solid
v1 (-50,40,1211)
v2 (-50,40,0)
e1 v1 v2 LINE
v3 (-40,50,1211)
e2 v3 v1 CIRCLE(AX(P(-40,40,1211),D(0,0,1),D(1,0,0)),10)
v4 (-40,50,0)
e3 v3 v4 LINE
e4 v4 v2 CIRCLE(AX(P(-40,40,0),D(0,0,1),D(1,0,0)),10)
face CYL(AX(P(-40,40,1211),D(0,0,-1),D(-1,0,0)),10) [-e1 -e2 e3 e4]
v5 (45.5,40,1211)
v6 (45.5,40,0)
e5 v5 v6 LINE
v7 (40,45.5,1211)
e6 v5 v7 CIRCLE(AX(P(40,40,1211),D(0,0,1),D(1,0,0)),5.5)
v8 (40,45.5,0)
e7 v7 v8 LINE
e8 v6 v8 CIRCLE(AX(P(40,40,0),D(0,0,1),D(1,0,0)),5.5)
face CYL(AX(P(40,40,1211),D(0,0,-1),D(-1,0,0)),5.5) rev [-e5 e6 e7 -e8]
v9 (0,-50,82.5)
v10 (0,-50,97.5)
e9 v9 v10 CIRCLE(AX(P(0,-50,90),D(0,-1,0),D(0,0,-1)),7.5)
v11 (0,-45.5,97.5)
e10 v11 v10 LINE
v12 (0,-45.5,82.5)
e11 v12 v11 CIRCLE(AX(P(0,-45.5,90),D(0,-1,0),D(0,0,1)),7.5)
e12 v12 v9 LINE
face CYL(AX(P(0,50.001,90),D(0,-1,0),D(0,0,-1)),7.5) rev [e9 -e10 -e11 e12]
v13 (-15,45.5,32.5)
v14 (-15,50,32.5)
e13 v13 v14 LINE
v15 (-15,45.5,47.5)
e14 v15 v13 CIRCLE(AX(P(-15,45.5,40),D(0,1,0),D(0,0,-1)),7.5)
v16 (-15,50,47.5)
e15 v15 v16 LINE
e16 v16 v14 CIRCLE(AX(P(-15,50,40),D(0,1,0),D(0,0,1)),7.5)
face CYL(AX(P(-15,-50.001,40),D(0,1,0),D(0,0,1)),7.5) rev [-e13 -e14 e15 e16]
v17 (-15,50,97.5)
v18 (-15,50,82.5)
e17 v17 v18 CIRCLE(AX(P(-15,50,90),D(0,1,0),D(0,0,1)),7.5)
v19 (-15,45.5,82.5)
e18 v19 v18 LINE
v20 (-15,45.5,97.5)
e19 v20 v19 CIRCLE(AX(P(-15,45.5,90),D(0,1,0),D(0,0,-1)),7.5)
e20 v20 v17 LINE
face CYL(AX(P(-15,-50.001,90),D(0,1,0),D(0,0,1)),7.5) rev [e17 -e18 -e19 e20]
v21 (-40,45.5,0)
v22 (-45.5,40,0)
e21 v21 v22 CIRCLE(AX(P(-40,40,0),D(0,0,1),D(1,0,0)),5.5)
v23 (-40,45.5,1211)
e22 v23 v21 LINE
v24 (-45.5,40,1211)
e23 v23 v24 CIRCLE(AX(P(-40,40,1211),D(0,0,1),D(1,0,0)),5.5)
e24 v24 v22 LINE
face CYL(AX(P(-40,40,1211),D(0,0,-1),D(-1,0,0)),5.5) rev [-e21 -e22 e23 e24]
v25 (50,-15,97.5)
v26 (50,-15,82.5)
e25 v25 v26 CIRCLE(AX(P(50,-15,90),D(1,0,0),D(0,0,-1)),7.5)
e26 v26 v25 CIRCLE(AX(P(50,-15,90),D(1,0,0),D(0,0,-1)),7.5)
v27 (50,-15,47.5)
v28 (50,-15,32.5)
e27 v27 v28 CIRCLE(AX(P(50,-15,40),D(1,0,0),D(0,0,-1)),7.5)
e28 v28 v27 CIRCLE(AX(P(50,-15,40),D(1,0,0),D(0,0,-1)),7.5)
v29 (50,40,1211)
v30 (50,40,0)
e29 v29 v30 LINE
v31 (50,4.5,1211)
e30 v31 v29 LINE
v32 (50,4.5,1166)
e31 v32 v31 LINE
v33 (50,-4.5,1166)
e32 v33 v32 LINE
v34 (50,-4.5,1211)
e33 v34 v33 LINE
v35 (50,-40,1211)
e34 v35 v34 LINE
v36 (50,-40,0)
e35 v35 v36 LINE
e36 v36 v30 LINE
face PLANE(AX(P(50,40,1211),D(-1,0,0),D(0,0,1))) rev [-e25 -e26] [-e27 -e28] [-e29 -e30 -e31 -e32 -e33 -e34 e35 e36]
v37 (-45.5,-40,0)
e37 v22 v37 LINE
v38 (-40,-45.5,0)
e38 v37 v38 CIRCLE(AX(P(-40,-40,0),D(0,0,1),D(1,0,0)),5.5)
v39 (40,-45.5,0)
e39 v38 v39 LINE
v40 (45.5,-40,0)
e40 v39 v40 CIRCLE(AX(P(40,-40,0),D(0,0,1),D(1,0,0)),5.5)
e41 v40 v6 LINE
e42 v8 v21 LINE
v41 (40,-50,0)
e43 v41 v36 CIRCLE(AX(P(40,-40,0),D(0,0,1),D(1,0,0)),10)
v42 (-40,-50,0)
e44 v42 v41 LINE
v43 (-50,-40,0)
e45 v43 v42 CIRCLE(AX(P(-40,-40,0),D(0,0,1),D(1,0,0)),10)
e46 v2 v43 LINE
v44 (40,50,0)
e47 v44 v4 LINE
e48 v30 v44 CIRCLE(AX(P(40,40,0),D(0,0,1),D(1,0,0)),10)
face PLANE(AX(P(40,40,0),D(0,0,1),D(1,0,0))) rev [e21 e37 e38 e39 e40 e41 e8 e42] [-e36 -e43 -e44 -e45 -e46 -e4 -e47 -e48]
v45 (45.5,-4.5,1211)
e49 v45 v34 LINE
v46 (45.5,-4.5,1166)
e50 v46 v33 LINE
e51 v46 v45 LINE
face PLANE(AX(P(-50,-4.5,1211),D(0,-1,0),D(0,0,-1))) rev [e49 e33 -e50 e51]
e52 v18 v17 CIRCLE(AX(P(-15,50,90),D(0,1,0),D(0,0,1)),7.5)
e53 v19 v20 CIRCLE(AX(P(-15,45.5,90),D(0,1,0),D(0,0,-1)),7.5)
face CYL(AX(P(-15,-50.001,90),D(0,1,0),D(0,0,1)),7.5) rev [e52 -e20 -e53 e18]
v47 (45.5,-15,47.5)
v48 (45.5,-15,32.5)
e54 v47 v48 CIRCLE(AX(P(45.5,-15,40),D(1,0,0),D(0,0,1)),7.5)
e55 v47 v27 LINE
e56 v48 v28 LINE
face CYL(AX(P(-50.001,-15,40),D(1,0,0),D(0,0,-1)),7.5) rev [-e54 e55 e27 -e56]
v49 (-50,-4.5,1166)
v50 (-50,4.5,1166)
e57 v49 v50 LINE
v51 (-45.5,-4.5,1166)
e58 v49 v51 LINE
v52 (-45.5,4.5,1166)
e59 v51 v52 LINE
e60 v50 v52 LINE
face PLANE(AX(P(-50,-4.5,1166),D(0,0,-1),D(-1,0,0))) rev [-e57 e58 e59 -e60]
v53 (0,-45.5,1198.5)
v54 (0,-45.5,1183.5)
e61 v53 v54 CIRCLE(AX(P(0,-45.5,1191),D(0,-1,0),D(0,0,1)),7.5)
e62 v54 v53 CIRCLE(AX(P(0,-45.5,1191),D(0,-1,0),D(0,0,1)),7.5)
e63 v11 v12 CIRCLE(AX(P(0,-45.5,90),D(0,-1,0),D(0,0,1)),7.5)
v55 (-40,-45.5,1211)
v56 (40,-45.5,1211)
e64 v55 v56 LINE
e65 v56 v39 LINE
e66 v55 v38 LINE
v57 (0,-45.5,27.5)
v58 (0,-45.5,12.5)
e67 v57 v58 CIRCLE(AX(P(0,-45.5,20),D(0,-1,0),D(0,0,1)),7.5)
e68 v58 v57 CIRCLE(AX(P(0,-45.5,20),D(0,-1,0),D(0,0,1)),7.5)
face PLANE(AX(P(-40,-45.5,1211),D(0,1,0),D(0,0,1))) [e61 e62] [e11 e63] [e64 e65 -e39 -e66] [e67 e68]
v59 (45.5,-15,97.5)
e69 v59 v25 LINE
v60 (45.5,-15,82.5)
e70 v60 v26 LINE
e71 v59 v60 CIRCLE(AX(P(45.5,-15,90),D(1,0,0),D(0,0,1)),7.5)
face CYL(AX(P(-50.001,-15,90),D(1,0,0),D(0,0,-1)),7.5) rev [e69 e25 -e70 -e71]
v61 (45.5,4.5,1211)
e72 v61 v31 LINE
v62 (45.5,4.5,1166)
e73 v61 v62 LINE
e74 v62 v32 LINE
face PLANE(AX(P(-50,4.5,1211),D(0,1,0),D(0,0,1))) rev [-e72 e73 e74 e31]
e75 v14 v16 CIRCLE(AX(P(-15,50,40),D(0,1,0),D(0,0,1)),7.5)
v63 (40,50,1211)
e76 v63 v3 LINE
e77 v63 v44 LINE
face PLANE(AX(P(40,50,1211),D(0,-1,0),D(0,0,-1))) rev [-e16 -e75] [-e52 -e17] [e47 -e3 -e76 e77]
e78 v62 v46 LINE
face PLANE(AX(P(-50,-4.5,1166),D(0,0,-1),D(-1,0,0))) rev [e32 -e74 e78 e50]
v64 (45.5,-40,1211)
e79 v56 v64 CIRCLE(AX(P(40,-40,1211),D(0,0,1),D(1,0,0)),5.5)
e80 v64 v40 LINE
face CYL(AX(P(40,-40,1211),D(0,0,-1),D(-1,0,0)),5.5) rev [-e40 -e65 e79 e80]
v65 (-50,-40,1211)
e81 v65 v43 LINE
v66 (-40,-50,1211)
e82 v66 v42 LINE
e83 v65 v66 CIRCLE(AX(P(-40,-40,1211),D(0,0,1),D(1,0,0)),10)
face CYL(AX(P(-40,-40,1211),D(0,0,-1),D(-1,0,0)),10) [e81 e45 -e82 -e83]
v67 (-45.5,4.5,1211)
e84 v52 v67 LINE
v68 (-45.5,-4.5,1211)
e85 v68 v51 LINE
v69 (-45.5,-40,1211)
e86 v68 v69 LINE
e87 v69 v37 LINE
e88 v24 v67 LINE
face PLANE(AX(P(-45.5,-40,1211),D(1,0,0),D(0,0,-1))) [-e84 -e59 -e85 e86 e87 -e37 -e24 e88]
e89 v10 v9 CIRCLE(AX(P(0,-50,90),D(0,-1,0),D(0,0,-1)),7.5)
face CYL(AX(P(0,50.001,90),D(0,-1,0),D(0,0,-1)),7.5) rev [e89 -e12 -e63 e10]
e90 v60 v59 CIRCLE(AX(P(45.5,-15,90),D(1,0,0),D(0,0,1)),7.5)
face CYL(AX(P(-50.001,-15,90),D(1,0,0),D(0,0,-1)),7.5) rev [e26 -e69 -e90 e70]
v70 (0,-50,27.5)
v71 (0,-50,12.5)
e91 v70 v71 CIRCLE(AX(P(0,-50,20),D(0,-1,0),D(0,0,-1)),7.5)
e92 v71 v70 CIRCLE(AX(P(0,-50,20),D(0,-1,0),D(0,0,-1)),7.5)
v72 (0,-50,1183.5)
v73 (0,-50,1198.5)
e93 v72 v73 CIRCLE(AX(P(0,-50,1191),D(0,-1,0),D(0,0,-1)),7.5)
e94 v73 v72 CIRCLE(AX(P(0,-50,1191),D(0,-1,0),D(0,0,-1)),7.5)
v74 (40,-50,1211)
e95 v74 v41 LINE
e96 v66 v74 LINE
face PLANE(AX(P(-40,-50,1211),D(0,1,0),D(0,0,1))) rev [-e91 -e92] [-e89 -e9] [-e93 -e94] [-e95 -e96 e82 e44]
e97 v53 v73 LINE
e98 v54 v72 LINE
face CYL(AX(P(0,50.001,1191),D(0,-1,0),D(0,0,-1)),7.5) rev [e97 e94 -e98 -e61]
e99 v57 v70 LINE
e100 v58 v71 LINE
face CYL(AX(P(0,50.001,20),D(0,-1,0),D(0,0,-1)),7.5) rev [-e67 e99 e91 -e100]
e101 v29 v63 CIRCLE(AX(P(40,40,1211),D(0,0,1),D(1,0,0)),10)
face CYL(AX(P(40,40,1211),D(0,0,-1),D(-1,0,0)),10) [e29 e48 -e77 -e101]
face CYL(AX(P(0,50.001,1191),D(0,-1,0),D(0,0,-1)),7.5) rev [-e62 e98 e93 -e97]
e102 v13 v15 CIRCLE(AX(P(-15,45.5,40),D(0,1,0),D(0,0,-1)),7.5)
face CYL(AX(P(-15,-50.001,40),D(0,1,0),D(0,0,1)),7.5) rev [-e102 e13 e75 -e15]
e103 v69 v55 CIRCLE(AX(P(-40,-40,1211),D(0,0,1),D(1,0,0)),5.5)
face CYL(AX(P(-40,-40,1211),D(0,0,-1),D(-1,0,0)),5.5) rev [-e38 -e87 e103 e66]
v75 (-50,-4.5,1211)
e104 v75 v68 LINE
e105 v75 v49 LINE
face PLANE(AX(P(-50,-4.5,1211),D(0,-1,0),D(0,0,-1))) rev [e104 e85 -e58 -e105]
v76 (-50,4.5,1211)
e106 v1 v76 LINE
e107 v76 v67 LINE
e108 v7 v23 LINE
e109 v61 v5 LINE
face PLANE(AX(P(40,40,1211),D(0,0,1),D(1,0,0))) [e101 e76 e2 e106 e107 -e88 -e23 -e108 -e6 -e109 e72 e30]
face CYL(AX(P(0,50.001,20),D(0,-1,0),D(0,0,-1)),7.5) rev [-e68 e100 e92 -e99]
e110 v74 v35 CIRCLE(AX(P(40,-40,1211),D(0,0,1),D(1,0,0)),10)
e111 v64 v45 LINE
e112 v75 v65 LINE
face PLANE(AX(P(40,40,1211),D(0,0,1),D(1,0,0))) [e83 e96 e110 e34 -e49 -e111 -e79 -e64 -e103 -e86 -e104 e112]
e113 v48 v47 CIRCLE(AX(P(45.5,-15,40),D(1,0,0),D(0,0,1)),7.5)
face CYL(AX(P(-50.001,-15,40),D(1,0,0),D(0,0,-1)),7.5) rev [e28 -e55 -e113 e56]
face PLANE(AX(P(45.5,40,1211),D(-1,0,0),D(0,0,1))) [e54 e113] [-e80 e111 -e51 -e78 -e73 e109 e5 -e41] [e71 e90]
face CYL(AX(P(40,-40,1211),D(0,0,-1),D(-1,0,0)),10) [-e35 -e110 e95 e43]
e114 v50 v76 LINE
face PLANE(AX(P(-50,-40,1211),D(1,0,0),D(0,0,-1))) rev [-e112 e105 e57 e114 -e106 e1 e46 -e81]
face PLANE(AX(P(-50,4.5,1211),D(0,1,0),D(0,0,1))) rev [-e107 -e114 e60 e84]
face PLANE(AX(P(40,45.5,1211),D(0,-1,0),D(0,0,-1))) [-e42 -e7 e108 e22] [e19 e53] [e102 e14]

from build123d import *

# Parameters (mm, degrees)
BOSS_EXTRUDE1_DEPTH = 1211
CUT_EXTRUDE1_REACH  = 1218.15
SKETCH_1_R          = 7.5
CUT_EXTRUDE2_REACH  = 1218.15
SKETCH2_R           = 7.5
CUT_EXTRUDE3_REACH  = 1218.15
SKETCH3_R           = 7.5
SKETCH4_W           = 45
SKETCH4_H           = 9
CUT_EXTRUDE4_DEPTH  = 1217.150072976


with BuildPart() as part:
    # Sketch1 → Boss-Extrude1 (new body)
    with BuildSketch(Plane.XY):
        with BuildLine():
            Line((-40, -50), (40, -50))
            ThreePointArc((40, -50), (47.071067812, -47.071067812), (50, -40))
            Line((50, -40), (50, 40))
            ThreePointArc((50, 40), (47.071067812, 47.071067812), (40, 50))
            Line((40, 50), (-40, 50))
            ThreePointArc((-40, 50), (-47.071067812, 47.071067812), (-50, 40))
            Line((-50, 40), (-50, -40))
            ThreePointArc((-50, -40), (-47.071067812, -47.071067812), (-40, -50))
        make_face()
        with BuildLine():
            Line((-40, -45.5), (40, -45.5))
            ThreePointArc((40, -45.5), (43.889087297, -43.889087297), (45.5, -40))
            Line((45.5, -40), (45.5, 40))
            ThreePointArc((45.5, 40), (43.889087297, 43.889087297), (40, 45.5))
            Line((40, 45.5), (-40, 45.5))
            ThreePointArc((-40, 45.5), (-43.889087297, 43.889087297), (-45.5, 40))
            Line((-45.5, 40), (-45.5, -40))
            ThreePointArc((-45.5, -40), (-43.889087297, -43.889087297), (-40, -45.5))
        make_face(mode=Mode.SUBTRACT)
    extrude(amount=BOSS_EXTRUDE1_DEPTH)

    # 草图1 → Cut-Extrude1 (cut, up to next)
    with BuildSketch(Plane(origin=(50, 0, 0), x_dir=(0, 0, -1), z_dir=(1, 0, 0)), mode=Mode.PRIVATE) as cut_extrude1_sk1:
        with Locations((-40, -15)):
            Circle(SKETCH_1_R)
    cut_extrude1_tool1 = extrude(cut_extrude1_sk1.sketch, amount=-CUT_EXTRUDE1_REACH, mode=Mode.PRIVATE) & part.part
    # 草图1 → Cut-Extrude1 (cut, up to next)
    with BuildSketch(Plane(origin=(50, 0, 0), x_dir=(0, 0, -1), z_dir=(1, 0, 0)), mode=Mode.PRIVATE) as cut_extrude1_sk2:
        with Locations((-90, -15)):
            Circle(SKETCH_1_R)
    cut_extrude1_tool2 = extrude(cut_extrude1_sk2.sketch, amount=-CUT_EXTRUDE1_REACH, mode=Mode.PRIVATE) & part.part
    add(cut_extrude1_tool1.solids().sort_by_distance((50, -15, 40))[0], mode=Mode.SUBTRACT)
    add(cut_extrude1_tool2.solids().sort_by_distance((50, -15, 90))[0], mode=Mode.SUBTRACT)

    # Sketch2 → Cut-Extrude2 (cut, up to next)
    with BuildSketch(Plane.XZ.offset(50), mode=Mode.PRIVATE) as cut_extrude2_sk1:
        with Locations(Location((0, 20, 0), (0, 0, 270))):
            Circle(SKETCH2_R)
    cut_extrude2_tool1 = extrude(cut_extrude2_sk1.sketch, amount=-CUT_EXTRUDE2_REACH, mode=Mode.PRIVATE) & part.part
    # Sketch2 → Cut-Extrude2 (cut, up to next)
    with BuildSketch(Plane.XZ.offset(50), mode=Mode.PRIVATE) as cut_extrude2_sk2:
        with Locations(Location((0, 90, 0), (0, 0, 270))):
            Circle(SKETCH2_R)
    cut_extrude2_tool2 = extrude(cut_extrude2_sk2.sketch, amount=-CUT_EXTRUDE2_REACH, mode=Mode.PRIVATE) & part.part
    # Sketch2 → Cut-Extrude2 (cut, up to next)
    with BuildSketch(Plane.XZ.offset(50), mode=Mode.PRIVATE) as cut_extrude2_sk3:
        with Locations(Location((0, 1191, 0), (0, 0, 270))):
            Circle(SKETCH2_R)
    cut_extrude2_tool3 = extrude(cut_extrude2_sk3.sketch, amount=-CUT_EXTRUDE2_REACH, mode=Mode.PRIVATE) & part.part
    add(cut_extrude2_tool1.solids().sort_by_distance((0, -50, 20))[0], mode=Mode.SUBTRACT)
    add(cut_extrude2_tool2.solids().sort_by_distance((0, -50, 90))[0], mode=Mode.SUBTRACT)
    add(cut_extrude2_tool3.solids().sort_by_distance((0, -50, 1191))[0], mode=Mode.SUBTRACT)

    # Sketch3 → Cut-Extrude3 (cut, up to next)
    with BuildSketch(Plane(origin=(0, 50, 0), x_dir=(1, 0, 0), z_dir=(0, 1, 0)), mode=Mode.PRIVATE) as cut_extrude3_sk1:
        with Locations(Location((-15, -40, 0), (0, 0, 270))):
            Circle(SKETCH3_R)
    cut_extrude3_tool1 = extrude(cut_extrude3_sk1.sketch, amount=-CUT_EXTRUDE3_REACH, mode=Mode.PRIVATE) & part.part
    # Sketch3 → Cut-Extrude3 (cut, up to next)
    with BuildSketch(Plane(origin=(0, 50, 0), x_dir=(1, 0, 0), z_dir=(0, 1, 0)), mode=Mode.PRIVATE) as cut_extrude3_sk2:
        with Locations(Location((-15, -90, 0), (0, 0, 270))):
            Circle(SKETCH3_R)
    cut_extrude3_tool2 = extrude(cut_extrude3_sk2.sketch, amount=-CUT_EXTRUDE3_REACH, mode=Mode.PRIVATE) & part.part
    add(cut_extrude3_tool1.solids().sort_by_distance((-15, 50, 40))[0], mode=Mode.SUBTRACT)
    add(cut_extrude3_tool2.solids().sort_by_distance((-15, 50, 90))[0], mode=Mode.SUBTRACT)

    # Sketch4 → Cut-Extrude4 (cut, through all)
    with BuildSketch(Plane(origin=(50, 0, 0), x_dir=(0, 0, -1), z_dir=(1, 0, 0))):
        with Locations((-1188.5, 0)):
            Rectangle(SKETCH4_W, SKETCH4_H)
    extrude(amount=-CUT_EXTRUDE4_DEPTH, mode=Mode.SUBTRACT)


solid = part.part
